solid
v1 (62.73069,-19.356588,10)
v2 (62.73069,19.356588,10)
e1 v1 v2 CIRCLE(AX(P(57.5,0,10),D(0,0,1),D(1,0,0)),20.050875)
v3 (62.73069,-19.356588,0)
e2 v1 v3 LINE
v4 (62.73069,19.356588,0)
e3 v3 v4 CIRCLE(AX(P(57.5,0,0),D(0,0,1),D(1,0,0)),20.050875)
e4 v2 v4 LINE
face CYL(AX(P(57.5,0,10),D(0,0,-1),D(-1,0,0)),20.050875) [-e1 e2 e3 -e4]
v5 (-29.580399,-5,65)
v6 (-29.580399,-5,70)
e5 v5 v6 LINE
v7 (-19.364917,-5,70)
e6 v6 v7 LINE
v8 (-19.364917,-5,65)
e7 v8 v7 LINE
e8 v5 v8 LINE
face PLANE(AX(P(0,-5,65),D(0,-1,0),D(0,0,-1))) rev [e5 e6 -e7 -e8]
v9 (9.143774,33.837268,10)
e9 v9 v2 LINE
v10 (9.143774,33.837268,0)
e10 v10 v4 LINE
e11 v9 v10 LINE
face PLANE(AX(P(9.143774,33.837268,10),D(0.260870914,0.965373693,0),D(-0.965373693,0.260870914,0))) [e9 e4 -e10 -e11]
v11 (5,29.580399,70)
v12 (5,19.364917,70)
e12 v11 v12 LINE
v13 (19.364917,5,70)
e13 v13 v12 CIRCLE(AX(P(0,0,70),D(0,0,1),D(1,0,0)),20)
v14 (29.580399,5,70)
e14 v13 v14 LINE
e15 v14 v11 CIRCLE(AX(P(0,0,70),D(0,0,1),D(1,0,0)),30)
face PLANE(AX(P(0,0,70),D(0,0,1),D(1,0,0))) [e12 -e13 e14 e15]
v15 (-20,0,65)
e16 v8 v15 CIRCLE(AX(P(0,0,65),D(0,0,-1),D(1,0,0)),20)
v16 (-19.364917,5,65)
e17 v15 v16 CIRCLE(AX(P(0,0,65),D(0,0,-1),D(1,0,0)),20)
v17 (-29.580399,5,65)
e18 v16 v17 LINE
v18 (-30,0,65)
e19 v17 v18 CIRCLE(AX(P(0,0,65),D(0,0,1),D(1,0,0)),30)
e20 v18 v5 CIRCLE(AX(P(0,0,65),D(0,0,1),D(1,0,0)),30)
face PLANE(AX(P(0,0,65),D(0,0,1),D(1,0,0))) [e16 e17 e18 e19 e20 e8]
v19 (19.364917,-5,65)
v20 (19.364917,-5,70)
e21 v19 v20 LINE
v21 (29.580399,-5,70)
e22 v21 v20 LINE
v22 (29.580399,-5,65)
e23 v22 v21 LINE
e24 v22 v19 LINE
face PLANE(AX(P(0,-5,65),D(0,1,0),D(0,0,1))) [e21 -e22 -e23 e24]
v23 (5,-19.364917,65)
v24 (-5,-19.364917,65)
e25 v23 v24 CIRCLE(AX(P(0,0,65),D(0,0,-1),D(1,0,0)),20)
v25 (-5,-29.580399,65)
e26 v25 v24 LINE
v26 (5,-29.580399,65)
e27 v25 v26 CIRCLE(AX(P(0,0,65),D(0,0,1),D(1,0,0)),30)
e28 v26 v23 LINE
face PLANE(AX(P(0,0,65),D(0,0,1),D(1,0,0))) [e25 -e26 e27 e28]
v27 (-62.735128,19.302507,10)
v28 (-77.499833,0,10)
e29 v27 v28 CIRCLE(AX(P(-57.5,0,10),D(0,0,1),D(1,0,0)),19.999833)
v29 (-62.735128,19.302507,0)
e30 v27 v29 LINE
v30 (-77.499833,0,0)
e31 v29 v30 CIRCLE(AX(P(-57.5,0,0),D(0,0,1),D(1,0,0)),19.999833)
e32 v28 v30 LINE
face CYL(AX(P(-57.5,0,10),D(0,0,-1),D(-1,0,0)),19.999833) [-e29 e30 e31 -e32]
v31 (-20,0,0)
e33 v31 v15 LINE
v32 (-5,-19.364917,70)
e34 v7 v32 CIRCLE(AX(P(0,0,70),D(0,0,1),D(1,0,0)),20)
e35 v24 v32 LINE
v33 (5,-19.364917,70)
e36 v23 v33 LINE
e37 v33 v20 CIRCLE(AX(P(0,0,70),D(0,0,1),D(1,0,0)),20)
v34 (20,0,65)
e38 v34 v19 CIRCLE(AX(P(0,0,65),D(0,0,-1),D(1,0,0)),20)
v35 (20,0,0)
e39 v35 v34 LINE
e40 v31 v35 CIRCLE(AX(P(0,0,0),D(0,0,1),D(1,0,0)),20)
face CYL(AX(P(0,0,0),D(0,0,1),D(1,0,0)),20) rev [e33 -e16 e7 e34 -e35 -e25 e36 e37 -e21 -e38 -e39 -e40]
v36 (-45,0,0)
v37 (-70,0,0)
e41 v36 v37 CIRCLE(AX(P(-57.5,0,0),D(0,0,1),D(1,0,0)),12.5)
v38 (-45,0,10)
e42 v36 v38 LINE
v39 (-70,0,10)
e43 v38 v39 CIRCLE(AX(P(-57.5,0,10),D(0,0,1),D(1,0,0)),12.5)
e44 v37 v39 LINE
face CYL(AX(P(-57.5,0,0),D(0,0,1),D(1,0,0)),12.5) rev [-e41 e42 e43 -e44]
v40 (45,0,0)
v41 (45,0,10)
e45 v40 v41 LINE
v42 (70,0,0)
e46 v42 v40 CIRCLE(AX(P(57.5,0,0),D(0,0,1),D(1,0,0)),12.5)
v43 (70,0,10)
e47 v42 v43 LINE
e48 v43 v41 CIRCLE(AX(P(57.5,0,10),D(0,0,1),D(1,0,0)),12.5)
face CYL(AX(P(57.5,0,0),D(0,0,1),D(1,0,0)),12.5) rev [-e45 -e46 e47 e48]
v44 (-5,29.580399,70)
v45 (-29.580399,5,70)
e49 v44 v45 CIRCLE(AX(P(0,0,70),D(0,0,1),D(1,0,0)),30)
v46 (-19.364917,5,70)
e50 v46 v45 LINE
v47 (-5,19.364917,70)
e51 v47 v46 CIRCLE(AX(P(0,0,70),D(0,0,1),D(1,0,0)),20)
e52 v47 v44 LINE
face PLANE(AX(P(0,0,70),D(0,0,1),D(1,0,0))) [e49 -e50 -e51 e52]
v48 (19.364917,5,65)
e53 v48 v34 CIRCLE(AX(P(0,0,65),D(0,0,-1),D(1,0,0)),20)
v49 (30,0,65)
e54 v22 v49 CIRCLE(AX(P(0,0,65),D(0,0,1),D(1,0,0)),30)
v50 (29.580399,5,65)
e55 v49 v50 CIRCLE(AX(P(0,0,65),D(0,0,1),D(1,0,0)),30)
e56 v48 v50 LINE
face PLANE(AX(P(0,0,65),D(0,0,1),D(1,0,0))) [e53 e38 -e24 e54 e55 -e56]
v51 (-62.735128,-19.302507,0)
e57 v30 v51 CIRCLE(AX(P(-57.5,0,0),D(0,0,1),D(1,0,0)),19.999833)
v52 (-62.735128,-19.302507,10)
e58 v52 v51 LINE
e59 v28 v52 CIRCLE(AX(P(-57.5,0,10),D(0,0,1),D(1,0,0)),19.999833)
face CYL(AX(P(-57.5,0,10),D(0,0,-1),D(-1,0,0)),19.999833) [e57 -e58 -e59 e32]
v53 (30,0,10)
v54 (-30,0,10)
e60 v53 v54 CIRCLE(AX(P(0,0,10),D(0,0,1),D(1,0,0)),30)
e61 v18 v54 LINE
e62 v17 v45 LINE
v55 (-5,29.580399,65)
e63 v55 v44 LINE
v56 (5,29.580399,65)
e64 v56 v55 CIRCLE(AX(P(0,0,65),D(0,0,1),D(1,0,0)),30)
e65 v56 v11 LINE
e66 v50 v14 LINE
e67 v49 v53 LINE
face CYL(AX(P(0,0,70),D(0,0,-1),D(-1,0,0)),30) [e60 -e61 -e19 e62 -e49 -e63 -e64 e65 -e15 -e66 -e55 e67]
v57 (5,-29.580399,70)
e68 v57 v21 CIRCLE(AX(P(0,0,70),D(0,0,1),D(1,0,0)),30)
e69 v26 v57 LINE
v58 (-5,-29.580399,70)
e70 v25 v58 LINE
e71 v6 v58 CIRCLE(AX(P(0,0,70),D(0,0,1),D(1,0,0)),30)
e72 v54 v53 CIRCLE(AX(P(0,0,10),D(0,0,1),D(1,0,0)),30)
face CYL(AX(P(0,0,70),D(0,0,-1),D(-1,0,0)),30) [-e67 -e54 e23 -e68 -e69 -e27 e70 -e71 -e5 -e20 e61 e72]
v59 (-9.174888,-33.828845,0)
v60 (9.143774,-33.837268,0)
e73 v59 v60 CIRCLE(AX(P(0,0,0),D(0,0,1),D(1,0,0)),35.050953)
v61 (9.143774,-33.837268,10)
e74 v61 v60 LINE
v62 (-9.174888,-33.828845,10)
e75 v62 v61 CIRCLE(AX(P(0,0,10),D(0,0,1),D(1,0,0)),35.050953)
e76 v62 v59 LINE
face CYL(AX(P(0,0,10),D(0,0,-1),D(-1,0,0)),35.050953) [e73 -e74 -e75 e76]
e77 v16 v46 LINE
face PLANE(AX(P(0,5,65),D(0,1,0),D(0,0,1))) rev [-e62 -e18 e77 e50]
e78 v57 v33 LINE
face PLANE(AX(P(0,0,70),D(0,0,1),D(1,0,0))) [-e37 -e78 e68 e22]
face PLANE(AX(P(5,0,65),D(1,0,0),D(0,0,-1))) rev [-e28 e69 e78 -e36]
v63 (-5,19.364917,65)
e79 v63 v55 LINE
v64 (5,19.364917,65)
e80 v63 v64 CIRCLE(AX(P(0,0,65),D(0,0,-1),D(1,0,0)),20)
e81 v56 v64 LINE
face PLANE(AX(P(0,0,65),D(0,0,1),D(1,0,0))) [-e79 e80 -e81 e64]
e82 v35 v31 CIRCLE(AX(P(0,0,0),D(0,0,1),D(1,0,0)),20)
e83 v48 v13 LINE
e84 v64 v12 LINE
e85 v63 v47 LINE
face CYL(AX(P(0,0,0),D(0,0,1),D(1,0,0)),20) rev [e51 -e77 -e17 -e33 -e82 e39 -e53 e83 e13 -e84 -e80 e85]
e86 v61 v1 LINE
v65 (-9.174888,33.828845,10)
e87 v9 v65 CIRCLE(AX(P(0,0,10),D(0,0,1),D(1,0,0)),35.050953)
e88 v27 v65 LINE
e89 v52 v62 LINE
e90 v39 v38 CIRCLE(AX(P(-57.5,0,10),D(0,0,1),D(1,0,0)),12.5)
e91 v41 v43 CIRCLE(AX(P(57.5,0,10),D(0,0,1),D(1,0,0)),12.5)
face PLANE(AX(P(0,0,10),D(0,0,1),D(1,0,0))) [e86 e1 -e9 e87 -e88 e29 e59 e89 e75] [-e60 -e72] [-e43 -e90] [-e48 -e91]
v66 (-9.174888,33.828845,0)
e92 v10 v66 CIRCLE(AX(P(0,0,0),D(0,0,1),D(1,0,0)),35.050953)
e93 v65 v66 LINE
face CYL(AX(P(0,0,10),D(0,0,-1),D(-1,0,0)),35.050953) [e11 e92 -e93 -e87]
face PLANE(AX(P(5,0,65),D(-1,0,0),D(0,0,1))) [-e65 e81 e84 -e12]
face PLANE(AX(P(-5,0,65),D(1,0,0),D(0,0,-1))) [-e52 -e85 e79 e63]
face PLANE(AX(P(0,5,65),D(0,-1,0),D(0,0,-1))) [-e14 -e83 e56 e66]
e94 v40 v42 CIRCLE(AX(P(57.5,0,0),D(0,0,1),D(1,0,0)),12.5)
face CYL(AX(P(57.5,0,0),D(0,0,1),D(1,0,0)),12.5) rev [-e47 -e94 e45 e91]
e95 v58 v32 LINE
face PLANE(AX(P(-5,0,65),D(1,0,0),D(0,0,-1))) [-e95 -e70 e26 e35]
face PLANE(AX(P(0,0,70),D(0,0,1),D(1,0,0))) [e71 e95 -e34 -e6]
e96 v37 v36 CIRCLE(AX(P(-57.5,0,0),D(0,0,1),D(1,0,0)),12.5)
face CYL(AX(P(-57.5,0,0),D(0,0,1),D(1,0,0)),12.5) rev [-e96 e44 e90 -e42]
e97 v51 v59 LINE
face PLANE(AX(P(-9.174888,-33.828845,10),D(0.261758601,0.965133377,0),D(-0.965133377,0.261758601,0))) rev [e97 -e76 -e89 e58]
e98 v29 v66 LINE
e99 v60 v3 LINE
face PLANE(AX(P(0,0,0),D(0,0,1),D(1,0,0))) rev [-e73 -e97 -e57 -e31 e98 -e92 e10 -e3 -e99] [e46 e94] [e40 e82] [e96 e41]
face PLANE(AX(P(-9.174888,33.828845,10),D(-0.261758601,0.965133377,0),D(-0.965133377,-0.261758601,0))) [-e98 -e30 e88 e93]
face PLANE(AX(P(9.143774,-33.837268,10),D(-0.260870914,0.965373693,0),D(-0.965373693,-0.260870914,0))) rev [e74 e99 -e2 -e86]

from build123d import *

# Parameters (mm, degrees)
FLANGE_PLATE_DEPTH      = 10
CYLINDER_BOSS_SKETCH_R  = 30
CYLINDER_BOSS_DEPTH     = 60
BORE_SKETCH_R           = 20
THROUGH_BORE_DEPTH      = 70
END_SLOTS_SKETCH_W      = 10
END_SLOTS_SKETCH_H      = 12.639410213
END_SLOTS_SKETCH_H_2    = 13.280913302
END_SLOTS_SKETCH_W_2    = 15.451741121
END_SLOTS_SKETCH_H_3    = 10
END_SLOTS_SKETCH_W_3    = 12.65016047
END_SLOTS_4X_DEPTH      = 5
MOUNTING_HOLES_SKETCH_R = 12.5
MOUNTING_HOLES_2X_DEPTH = 10


with BuildPart() as part:
    # Flange Plate Sketch → Flange Plate (new body)
    with BuildSketch(Plane.XY):
        with BuildLine():
            Line((9.143774129, 33.837267894), (62.730690194, 19.356587648))
            ThreePointArc((62.730690194, 19.356587648), (77.550875425, 0), (62.730690194, -19.356587648))
            Line((62.730690194, -19.356587648), (9.143774129, -33.837267894))
            ThreePointArc((9.143774129, -33.837267894), (-0.016117163, -35.050949261), (-9.174888429, -33.828844588))
            Line((-9.174888429, -33.828844588), (-62.735128416, -19.302506721))
            ThreePointArc((-62.735128416, -19.302506721), (-77.49983338, 0), (-62.735128416, 19.302506721))
            Line((-62.735128416, 19.302506721), (-9.174888429, 33.828844588))
            ThreePointArc((-9.174888429, 33.828844588), (-0.016117163, 35.050949261), (9.143774129, 33.837267894))
        make_face()
    extrude(amount=FLANGE_PLATE_DEPTH)

    # Cylinder Boss Sketch → Cylinder Boss (add)
    with BuildSketch(Plane.XY.offset(10)):
        Circle(CYLINDER_BOSS_SKETCH_R)
    extrude(amount=CYLINDER_BOSS_DEPTH)

    # Bore Sketch → Through Bore (cut)
    with BuildSketch(Plane.XY.offset(70)):
        Circle(BORE_SKETCH_R)
    extrude(amount=-THROUGH_BORE_DEPTH, mode=Mode.SUBTRACT)

    # End Slots Sketch → End Slots 4x (cut)
    with BuildSketch(Plane.XY.offset(70)):
        with Locations((0, 23.680294894)):
            Rectangle(END_SLOTS_SKETCH_W, END_SLOTS_SKETCH_H)
        with Locations((0, -23.359543349)):
            Rectangle(END_SLOTS_SKETCH_W, END_SLOTS_SKETCH_H_2)
        with Locations((-22.27412944, 0)):
            Rectangle(END_SLOTS_SKETCH_W_2, END_SLOTS_SKETCH_H_3)
        with Locations((23.674919765, 0)):
            Rectangle(END_SLOTS_SKETCH_W_3, END_SLOTS_SKETCH_H_3)
    extrude(amount=-END_SLOTS_4X_DEPTH, mode=Mode.SUBTRACT)

    # Mounting Holes Sketch → Mounting Holes 2x (cut)
    with BuildSketch(Plane.XY.offset(10)):
        with Locations((-57.5, 0)):
            Circle(MOUNTING_HOLES_SKETCH_R)
        with Locations((57.5, 0)):
            Circle(MOUNTING_HOLES_SKETCH_R)
    extrude(amount=-MOUNTING_HOLES_2X_DEPTH, mode=Mode.SUBTRACT)


solid = part.part
